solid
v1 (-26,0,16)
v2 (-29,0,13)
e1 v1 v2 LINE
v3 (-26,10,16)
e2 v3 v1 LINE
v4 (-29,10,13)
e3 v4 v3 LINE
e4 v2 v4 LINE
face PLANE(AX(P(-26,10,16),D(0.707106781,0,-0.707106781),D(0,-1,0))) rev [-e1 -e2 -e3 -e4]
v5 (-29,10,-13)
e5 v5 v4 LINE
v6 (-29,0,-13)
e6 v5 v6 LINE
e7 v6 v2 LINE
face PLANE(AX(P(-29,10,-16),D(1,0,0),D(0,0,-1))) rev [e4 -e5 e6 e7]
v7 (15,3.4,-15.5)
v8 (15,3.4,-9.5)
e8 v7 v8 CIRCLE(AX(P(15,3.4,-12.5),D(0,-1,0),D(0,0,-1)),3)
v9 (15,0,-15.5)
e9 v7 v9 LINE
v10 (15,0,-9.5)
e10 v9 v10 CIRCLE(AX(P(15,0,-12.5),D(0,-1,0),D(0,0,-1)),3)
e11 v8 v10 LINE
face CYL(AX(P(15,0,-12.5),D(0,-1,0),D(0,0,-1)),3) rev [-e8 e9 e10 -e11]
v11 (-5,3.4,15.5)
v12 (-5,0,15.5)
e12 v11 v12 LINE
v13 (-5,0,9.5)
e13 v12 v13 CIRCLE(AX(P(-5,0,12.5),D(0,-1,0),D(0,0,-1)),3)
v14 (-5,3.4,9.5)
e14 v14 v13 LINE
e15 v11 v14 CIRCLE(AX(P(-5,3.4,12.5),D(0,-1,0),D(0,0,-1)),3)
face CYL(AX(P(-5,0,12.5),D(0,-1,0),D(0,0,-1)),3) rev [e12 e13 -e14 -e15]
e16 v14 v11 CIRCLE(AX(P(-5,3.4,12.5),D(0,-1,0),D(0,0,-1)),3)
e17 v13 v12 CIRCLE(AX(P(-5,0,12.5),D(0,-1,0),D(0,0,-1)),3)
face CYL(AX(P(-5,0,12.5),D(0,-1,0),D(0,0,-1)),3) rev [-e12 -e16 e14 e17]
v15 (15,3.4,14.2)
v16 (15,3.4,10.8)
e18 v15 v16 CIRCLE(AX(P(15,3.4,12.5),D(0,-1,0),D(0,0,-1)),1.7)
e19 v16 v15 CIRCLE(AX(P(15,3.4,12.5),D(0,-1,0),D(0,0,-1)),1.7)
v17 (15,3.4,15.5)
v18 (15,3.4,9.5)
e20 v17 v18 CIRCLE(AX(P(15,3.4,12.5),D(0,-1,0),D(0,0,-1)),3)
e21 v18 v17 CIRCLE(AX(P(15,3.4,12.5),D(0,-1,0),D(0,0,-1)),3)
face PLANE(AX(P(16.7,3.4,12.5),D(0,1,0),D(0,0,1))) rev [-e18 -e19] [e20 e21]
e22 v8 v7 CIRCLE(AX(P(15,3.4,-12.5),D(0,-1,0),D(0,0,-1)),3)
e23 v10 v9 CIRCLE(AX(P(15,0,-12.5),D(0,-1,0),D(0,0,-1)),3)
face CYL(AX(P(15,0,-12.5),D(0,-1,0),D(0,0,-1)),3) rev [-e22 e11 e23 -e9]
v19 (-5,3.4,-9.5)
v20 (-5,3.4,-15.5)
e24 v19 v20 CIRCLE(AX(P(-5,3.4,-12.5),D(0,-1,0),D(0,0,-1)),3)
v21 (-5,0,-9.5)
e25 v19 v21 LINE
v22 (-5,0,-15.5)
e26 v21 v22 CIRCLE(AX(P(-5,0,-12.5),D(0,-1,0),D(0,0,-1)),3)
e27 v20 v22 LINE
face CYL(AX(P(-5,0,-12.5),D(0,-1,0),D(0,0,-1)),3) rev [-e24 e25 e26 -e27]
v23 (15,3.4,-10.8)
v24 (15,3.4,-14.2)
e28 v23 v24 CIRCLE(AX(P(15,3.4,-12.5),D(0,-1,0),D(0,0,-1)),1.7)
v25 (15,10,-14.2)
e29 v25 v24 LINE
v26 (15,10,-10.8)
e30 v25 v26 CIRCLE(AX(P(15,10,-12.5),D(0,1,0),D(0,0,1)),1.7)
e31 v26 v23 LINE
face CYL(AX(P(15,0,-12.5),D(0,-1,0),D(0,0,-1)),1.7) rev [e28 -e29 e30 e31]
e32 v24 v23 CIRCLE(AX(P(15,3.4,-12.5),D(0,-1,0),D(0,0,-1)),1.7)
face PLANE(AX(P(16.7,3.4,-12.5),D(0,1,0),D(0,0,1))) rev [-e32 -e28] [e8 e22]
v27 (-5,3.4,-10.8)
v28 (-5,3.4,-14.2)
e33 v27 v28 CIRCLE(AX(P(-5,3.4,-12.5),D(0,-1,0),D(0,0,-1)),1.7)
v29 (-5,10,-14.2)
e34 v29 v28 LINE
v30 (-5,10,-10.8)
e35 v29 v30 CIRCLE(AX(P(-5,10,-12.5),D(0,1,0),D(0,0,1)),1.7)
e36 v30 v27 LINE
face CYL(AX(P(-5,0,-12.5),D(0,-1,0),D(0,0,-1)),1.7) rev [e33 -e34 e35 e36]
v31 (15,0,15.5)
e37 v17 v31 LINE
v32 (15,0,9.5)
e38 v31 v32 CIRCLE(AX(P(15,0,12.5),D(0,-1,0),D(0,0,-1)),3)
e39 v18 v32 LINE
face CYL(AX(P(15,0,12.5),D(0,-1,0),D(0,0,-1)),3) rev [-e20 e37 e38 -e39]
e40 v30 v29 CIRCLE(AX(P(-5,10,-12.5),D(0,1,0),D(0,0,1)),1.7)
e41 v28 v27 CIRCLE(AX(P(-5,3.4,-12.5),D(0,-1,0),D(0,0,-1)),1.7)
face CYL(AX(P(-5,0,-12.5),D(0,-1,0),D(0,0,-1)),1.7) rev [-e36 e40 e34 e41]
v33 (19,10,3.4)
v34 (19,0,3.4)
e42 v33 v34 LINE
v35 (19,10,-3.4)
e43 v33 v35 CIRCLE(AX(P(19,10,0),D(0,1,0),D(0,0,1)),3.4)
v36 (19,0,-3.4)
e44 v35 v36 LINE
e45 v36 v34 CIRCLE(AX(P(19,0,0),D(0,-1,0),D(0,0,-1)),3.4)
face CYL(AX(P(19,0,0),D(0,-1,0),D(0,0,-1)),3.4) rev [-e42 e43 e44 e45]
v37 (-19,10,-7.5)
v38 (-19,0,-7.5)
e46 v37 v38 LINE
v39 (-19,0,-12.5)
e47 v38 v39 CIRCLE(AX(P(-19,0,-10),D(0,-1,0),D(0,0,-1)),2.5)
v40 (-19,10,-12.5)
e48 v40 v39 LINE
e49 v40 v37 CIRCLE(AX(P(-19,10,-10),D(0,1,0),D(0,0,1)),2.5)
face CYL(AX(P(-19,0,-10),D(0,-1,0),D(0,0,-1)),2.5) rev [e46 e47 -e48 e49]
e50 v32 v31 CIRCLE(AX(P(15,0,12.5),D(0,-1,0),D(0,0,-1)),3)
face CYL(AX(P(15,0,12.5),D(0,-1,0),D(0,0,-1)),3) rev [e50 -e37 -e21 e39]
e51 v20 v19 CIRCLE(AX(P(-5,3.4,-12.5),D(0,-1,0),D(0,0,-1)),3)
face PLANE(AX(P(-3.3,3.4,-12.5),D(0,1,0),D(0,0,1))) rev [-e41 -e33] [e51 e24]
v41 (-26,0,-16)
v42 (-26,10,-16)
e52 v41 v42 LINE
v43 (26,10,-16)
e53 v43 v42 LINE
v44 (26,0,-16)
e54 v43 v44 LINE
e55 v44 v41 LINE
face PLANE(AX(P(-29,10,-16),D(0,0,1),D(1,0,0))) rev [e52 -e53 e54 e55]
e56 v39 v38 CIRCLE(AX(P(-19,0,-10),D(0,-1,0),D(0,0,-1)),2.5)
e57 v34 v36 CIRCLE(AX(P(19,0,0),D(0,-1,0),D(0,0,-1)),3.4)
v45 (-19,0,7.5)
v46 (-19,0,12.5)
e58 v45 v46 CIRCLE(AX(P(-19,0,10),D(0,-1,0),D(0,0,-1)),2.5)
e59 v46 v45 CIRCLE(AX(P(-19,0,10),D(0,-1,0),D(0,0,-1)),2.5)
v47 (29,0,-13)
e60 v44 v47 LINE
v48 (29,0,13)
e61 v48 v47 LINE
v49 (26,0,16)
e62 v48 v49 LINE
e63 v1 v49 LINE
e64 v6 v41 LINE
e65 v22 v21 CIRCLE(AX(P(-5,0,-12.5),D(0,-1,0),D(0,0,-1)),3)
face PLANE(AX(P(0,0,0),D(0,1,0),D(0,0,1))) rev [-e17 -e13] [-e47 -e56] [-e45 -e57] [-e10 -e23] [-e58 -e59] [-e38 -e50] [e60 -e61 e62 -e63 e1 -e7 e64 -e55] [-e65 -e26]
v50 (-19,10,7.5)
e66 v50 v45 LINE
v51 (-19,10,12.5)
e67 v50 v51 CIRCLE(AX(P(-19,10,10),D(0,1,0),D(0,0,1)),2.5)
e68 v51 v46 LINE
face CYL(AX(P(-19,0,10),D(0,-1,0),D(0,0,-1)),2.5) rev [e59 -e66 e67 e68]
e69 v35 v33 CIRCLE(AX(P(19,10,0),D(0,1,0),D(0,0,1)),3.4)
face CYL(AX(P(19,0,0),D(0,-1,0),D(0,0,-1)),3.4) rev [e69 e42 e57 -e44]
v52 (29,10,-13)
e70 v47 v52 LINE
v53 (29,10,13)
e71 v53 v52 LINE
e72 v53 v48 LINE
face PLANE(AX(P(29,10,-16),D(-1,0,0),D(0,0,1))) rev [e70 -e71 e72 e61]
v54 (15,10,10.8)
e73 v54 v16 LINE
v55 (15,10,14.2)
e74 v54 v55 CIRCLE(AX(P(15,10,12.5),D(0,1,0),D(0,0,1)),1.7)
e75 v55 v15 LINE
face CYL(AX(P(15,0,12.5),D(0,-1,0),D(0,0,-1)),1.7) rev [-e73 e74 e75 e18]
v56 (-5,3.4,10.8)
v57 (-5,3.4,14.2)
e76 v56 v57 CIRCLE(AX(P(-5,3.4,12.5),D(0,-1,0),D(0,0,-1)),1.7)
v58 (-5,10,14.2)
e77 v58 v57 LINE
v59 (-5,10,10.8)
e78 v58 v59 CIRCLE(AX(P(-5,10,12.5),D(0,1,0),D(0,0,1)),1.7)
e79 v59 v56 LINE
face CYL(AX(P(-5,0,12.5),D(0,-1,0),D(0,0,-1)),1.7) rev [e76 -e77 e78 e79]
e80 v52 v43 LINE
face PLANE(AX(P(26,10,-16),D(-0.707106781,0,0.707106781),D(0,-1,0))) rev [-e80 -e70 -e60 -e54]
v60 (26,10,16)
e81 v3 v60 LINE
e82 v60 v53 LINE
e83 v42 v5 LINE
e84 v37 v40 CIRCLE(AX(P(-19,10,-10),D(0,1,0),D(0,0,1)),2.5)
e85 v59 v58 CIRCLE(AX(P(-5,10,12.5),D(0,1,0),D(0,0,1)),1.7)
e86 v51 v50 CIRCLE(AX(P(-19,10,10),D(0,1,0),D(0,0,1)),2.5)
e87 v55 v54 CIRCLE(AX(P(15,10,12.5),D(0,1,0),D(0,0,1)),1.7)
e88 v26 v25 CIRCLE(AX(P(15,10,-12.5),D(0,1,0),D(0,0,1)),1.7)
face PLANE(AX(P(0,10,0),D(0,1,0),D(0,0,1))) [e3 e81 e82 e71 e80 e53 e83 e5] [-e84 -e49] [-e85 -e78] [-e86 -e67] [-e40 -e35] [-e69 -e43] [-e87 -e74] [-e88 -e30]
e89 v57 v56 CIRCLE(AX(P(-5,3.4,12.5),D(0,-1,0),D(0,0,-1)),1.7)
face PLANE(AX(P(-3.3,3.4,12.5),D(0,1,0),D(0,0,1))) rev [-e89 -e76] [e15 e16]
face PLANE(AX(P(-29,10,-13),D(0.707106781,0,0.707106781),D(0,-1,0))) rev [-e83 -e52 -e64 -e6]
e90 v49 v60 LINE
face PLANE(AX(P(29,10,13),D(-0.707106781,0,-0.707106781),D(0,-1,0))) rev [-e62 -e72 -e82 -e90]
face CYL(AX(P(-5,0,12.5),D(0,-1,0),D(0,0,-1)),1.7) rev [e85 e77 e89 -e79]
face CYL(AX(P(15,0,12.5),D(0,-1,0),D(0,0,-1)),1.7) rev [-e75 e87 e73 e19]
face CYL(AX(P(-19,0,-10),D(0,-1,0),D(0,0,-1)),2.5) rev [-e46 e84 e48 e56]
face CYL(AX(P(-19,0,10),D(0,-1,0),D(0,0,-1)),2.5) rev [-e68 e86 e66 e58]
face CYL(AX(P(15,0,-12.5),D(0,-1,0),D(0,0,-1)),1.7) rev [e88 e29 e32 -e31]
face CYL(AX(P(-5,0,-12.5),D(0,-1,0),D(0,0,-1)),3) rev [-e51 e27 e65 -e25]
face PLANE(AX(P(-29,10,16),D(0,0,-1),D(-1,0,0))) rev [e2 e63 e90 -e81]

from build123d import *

# Parameters (mm, degrees)
SKETCH1_W                                            = 58
SKETCH1_H                                            = 32
BOSS_EXTRUDE1_DEPTH                                  = 10
CBORE_FOR_M4_HEXAGON_SOCKET_HEAD_CAP_SCR_D           = 3.4
CBORE_FOR_M4_HEXAGON_SOCKET_HEAD_CAP_SCR_DEPTH       = 18.1
CBORE_FOR_M4_HEXAGON_SOCKET_HEAD_CAP_SCR_CBORE_D     = 6
CBORE_FOR_M4_HEXAGON_SOCKET_HEAD_CAP_SCR_CBORE_DEPTH = 3.4
CBORE_FOR_M4_HEXAGON_SOCKET_HEAD_CAP_SCR_TIP         = 1.021463052
M6_TAPPED_HOLE1_D                                    = 5
M6_TAPPED_HOLE1_DEPTH                                = 15
M6_TAPPED_HOLE1_TIP                                  = 1.502151548
M8_TAPPED_HOLE1_D                                    = 6.8
M8_TAPPED_HOLE1_DEPTH                                = 19.75
M8_TAPPED_HOLE1_TIP                                  = 2.042926105
CHAMFER1_SIZE                                        = 3


with BuildPart() as part:
    # Sketch1 → Boss-Extrude1 (new body)
    with BuildSketch(Plane(origin=(0, 0, 0), x_dir=(1, 0, 0), z_dir=(0, 1, 0))):
        Rectangle(SKETCH1_W, SKETCH1_H)
    extrude(amount=BOSS_EXTRUDE1_DEPTH)

    # CBORE for M4 Hexagon socket head cap screws1
    with Locations(Plane(origin=(0, 0, 0), x_dir=(-1, 0, 0), z_dir=(0, -1, 0))):
        with Locations((-15, 12.5), (5, 12.5), (-15, -12.5), (5, -12.5)):
            CounterBoreHole(CBORE_FOR_M4_HEXAGON_SOCKET_HEAD_CAP_SCR_D / 2, CBORE_FOR_M4_HEXAGON_SOCKET_HEAD_CAP_SCR_CBORE_D / 2, CBORE_FOR_M4_HEXAGON_SOCKET_HEAD_CAP_SCR_CBORE_DEPTH, depth=CBORE_FOR_M4_HEXAGON_SOCKET_HEAD_CAP_SCR_DEPTH)
            with Locations((0, 0, -(CBORE_FOR_M4_HEXAGON_SOCKET_HEAD_CAP_SCR_DEPTH + CBORE_FOR_M4_HEXAGON_SOCKET_HEAD_CAP_SCR_TIP / 2))):  # 118° drill point
                Cone(0, CBORE_FOR_M4_HEXAGON_SOCKET_HEAD_CAP_SCR_D / 2, CBORE_FOR_M4_HEXAGON_SOCKET_HEAD_CAP_SCR_TIP, mode=Mode.SUBTRACT)

    # M6 Tapped Hole1
    with Locations(Plane(origin=(0, 0, 0), x_dir=(-1, 0, 0), z_dir=(0, -1, 0))):
        with Locations((19, 10), (19, -10)):
            Hole(M6_TAPPED_HOLE1_D / 2, depth=M6_TAPPED_HOLE1_DEPTH)
            with Locations((0, 0, -(M6_TAPPED_HOLE1_DEPTH + M6_TAPPED_HOLE1_TIP / 2))):  # 118° drill point
                Cone(0, M6_TAPPED_HOLE1_D / 2, M6_TAPPED_HOLE1_TIP, mode=Mode.SUBTRACT)

    # M8 Tapped Hole1
    with Locations(Plane(origin=(0, 0, 0), x_dir=(-1, 0, 0), z_dir=(0, -1, 0))):
        with Locations((-19, 0)):
            Hole(M8_TAPPED_HOLE1_D / 2, depth=M8_TAPPED_HOLE1_DEPTH)
            with Locations((0, 0, -(M8_TAPPED_HOLE1_DEPTH + M8_TAPPED_HOLE1_TIP / 2))):  # 118° drill point
                Cone(0, M8_TAPPED_HOLE1_D / 2, M8_TAPPED_HOLE1_TIP, mode=Mode.SUBTRACT)

    # Chamfer1
    chamfer1_edges = [part.edges().sort_by_distance(p)[0] for p in [
        (29, 5, 16),
        (-29, 5, 16),
        (-29, 5, -16),
        (29, 5, -16),
    ]]
    chamfer(chamfer1_edges, length=CHAMFER1_SIZE)


solid = part.part
